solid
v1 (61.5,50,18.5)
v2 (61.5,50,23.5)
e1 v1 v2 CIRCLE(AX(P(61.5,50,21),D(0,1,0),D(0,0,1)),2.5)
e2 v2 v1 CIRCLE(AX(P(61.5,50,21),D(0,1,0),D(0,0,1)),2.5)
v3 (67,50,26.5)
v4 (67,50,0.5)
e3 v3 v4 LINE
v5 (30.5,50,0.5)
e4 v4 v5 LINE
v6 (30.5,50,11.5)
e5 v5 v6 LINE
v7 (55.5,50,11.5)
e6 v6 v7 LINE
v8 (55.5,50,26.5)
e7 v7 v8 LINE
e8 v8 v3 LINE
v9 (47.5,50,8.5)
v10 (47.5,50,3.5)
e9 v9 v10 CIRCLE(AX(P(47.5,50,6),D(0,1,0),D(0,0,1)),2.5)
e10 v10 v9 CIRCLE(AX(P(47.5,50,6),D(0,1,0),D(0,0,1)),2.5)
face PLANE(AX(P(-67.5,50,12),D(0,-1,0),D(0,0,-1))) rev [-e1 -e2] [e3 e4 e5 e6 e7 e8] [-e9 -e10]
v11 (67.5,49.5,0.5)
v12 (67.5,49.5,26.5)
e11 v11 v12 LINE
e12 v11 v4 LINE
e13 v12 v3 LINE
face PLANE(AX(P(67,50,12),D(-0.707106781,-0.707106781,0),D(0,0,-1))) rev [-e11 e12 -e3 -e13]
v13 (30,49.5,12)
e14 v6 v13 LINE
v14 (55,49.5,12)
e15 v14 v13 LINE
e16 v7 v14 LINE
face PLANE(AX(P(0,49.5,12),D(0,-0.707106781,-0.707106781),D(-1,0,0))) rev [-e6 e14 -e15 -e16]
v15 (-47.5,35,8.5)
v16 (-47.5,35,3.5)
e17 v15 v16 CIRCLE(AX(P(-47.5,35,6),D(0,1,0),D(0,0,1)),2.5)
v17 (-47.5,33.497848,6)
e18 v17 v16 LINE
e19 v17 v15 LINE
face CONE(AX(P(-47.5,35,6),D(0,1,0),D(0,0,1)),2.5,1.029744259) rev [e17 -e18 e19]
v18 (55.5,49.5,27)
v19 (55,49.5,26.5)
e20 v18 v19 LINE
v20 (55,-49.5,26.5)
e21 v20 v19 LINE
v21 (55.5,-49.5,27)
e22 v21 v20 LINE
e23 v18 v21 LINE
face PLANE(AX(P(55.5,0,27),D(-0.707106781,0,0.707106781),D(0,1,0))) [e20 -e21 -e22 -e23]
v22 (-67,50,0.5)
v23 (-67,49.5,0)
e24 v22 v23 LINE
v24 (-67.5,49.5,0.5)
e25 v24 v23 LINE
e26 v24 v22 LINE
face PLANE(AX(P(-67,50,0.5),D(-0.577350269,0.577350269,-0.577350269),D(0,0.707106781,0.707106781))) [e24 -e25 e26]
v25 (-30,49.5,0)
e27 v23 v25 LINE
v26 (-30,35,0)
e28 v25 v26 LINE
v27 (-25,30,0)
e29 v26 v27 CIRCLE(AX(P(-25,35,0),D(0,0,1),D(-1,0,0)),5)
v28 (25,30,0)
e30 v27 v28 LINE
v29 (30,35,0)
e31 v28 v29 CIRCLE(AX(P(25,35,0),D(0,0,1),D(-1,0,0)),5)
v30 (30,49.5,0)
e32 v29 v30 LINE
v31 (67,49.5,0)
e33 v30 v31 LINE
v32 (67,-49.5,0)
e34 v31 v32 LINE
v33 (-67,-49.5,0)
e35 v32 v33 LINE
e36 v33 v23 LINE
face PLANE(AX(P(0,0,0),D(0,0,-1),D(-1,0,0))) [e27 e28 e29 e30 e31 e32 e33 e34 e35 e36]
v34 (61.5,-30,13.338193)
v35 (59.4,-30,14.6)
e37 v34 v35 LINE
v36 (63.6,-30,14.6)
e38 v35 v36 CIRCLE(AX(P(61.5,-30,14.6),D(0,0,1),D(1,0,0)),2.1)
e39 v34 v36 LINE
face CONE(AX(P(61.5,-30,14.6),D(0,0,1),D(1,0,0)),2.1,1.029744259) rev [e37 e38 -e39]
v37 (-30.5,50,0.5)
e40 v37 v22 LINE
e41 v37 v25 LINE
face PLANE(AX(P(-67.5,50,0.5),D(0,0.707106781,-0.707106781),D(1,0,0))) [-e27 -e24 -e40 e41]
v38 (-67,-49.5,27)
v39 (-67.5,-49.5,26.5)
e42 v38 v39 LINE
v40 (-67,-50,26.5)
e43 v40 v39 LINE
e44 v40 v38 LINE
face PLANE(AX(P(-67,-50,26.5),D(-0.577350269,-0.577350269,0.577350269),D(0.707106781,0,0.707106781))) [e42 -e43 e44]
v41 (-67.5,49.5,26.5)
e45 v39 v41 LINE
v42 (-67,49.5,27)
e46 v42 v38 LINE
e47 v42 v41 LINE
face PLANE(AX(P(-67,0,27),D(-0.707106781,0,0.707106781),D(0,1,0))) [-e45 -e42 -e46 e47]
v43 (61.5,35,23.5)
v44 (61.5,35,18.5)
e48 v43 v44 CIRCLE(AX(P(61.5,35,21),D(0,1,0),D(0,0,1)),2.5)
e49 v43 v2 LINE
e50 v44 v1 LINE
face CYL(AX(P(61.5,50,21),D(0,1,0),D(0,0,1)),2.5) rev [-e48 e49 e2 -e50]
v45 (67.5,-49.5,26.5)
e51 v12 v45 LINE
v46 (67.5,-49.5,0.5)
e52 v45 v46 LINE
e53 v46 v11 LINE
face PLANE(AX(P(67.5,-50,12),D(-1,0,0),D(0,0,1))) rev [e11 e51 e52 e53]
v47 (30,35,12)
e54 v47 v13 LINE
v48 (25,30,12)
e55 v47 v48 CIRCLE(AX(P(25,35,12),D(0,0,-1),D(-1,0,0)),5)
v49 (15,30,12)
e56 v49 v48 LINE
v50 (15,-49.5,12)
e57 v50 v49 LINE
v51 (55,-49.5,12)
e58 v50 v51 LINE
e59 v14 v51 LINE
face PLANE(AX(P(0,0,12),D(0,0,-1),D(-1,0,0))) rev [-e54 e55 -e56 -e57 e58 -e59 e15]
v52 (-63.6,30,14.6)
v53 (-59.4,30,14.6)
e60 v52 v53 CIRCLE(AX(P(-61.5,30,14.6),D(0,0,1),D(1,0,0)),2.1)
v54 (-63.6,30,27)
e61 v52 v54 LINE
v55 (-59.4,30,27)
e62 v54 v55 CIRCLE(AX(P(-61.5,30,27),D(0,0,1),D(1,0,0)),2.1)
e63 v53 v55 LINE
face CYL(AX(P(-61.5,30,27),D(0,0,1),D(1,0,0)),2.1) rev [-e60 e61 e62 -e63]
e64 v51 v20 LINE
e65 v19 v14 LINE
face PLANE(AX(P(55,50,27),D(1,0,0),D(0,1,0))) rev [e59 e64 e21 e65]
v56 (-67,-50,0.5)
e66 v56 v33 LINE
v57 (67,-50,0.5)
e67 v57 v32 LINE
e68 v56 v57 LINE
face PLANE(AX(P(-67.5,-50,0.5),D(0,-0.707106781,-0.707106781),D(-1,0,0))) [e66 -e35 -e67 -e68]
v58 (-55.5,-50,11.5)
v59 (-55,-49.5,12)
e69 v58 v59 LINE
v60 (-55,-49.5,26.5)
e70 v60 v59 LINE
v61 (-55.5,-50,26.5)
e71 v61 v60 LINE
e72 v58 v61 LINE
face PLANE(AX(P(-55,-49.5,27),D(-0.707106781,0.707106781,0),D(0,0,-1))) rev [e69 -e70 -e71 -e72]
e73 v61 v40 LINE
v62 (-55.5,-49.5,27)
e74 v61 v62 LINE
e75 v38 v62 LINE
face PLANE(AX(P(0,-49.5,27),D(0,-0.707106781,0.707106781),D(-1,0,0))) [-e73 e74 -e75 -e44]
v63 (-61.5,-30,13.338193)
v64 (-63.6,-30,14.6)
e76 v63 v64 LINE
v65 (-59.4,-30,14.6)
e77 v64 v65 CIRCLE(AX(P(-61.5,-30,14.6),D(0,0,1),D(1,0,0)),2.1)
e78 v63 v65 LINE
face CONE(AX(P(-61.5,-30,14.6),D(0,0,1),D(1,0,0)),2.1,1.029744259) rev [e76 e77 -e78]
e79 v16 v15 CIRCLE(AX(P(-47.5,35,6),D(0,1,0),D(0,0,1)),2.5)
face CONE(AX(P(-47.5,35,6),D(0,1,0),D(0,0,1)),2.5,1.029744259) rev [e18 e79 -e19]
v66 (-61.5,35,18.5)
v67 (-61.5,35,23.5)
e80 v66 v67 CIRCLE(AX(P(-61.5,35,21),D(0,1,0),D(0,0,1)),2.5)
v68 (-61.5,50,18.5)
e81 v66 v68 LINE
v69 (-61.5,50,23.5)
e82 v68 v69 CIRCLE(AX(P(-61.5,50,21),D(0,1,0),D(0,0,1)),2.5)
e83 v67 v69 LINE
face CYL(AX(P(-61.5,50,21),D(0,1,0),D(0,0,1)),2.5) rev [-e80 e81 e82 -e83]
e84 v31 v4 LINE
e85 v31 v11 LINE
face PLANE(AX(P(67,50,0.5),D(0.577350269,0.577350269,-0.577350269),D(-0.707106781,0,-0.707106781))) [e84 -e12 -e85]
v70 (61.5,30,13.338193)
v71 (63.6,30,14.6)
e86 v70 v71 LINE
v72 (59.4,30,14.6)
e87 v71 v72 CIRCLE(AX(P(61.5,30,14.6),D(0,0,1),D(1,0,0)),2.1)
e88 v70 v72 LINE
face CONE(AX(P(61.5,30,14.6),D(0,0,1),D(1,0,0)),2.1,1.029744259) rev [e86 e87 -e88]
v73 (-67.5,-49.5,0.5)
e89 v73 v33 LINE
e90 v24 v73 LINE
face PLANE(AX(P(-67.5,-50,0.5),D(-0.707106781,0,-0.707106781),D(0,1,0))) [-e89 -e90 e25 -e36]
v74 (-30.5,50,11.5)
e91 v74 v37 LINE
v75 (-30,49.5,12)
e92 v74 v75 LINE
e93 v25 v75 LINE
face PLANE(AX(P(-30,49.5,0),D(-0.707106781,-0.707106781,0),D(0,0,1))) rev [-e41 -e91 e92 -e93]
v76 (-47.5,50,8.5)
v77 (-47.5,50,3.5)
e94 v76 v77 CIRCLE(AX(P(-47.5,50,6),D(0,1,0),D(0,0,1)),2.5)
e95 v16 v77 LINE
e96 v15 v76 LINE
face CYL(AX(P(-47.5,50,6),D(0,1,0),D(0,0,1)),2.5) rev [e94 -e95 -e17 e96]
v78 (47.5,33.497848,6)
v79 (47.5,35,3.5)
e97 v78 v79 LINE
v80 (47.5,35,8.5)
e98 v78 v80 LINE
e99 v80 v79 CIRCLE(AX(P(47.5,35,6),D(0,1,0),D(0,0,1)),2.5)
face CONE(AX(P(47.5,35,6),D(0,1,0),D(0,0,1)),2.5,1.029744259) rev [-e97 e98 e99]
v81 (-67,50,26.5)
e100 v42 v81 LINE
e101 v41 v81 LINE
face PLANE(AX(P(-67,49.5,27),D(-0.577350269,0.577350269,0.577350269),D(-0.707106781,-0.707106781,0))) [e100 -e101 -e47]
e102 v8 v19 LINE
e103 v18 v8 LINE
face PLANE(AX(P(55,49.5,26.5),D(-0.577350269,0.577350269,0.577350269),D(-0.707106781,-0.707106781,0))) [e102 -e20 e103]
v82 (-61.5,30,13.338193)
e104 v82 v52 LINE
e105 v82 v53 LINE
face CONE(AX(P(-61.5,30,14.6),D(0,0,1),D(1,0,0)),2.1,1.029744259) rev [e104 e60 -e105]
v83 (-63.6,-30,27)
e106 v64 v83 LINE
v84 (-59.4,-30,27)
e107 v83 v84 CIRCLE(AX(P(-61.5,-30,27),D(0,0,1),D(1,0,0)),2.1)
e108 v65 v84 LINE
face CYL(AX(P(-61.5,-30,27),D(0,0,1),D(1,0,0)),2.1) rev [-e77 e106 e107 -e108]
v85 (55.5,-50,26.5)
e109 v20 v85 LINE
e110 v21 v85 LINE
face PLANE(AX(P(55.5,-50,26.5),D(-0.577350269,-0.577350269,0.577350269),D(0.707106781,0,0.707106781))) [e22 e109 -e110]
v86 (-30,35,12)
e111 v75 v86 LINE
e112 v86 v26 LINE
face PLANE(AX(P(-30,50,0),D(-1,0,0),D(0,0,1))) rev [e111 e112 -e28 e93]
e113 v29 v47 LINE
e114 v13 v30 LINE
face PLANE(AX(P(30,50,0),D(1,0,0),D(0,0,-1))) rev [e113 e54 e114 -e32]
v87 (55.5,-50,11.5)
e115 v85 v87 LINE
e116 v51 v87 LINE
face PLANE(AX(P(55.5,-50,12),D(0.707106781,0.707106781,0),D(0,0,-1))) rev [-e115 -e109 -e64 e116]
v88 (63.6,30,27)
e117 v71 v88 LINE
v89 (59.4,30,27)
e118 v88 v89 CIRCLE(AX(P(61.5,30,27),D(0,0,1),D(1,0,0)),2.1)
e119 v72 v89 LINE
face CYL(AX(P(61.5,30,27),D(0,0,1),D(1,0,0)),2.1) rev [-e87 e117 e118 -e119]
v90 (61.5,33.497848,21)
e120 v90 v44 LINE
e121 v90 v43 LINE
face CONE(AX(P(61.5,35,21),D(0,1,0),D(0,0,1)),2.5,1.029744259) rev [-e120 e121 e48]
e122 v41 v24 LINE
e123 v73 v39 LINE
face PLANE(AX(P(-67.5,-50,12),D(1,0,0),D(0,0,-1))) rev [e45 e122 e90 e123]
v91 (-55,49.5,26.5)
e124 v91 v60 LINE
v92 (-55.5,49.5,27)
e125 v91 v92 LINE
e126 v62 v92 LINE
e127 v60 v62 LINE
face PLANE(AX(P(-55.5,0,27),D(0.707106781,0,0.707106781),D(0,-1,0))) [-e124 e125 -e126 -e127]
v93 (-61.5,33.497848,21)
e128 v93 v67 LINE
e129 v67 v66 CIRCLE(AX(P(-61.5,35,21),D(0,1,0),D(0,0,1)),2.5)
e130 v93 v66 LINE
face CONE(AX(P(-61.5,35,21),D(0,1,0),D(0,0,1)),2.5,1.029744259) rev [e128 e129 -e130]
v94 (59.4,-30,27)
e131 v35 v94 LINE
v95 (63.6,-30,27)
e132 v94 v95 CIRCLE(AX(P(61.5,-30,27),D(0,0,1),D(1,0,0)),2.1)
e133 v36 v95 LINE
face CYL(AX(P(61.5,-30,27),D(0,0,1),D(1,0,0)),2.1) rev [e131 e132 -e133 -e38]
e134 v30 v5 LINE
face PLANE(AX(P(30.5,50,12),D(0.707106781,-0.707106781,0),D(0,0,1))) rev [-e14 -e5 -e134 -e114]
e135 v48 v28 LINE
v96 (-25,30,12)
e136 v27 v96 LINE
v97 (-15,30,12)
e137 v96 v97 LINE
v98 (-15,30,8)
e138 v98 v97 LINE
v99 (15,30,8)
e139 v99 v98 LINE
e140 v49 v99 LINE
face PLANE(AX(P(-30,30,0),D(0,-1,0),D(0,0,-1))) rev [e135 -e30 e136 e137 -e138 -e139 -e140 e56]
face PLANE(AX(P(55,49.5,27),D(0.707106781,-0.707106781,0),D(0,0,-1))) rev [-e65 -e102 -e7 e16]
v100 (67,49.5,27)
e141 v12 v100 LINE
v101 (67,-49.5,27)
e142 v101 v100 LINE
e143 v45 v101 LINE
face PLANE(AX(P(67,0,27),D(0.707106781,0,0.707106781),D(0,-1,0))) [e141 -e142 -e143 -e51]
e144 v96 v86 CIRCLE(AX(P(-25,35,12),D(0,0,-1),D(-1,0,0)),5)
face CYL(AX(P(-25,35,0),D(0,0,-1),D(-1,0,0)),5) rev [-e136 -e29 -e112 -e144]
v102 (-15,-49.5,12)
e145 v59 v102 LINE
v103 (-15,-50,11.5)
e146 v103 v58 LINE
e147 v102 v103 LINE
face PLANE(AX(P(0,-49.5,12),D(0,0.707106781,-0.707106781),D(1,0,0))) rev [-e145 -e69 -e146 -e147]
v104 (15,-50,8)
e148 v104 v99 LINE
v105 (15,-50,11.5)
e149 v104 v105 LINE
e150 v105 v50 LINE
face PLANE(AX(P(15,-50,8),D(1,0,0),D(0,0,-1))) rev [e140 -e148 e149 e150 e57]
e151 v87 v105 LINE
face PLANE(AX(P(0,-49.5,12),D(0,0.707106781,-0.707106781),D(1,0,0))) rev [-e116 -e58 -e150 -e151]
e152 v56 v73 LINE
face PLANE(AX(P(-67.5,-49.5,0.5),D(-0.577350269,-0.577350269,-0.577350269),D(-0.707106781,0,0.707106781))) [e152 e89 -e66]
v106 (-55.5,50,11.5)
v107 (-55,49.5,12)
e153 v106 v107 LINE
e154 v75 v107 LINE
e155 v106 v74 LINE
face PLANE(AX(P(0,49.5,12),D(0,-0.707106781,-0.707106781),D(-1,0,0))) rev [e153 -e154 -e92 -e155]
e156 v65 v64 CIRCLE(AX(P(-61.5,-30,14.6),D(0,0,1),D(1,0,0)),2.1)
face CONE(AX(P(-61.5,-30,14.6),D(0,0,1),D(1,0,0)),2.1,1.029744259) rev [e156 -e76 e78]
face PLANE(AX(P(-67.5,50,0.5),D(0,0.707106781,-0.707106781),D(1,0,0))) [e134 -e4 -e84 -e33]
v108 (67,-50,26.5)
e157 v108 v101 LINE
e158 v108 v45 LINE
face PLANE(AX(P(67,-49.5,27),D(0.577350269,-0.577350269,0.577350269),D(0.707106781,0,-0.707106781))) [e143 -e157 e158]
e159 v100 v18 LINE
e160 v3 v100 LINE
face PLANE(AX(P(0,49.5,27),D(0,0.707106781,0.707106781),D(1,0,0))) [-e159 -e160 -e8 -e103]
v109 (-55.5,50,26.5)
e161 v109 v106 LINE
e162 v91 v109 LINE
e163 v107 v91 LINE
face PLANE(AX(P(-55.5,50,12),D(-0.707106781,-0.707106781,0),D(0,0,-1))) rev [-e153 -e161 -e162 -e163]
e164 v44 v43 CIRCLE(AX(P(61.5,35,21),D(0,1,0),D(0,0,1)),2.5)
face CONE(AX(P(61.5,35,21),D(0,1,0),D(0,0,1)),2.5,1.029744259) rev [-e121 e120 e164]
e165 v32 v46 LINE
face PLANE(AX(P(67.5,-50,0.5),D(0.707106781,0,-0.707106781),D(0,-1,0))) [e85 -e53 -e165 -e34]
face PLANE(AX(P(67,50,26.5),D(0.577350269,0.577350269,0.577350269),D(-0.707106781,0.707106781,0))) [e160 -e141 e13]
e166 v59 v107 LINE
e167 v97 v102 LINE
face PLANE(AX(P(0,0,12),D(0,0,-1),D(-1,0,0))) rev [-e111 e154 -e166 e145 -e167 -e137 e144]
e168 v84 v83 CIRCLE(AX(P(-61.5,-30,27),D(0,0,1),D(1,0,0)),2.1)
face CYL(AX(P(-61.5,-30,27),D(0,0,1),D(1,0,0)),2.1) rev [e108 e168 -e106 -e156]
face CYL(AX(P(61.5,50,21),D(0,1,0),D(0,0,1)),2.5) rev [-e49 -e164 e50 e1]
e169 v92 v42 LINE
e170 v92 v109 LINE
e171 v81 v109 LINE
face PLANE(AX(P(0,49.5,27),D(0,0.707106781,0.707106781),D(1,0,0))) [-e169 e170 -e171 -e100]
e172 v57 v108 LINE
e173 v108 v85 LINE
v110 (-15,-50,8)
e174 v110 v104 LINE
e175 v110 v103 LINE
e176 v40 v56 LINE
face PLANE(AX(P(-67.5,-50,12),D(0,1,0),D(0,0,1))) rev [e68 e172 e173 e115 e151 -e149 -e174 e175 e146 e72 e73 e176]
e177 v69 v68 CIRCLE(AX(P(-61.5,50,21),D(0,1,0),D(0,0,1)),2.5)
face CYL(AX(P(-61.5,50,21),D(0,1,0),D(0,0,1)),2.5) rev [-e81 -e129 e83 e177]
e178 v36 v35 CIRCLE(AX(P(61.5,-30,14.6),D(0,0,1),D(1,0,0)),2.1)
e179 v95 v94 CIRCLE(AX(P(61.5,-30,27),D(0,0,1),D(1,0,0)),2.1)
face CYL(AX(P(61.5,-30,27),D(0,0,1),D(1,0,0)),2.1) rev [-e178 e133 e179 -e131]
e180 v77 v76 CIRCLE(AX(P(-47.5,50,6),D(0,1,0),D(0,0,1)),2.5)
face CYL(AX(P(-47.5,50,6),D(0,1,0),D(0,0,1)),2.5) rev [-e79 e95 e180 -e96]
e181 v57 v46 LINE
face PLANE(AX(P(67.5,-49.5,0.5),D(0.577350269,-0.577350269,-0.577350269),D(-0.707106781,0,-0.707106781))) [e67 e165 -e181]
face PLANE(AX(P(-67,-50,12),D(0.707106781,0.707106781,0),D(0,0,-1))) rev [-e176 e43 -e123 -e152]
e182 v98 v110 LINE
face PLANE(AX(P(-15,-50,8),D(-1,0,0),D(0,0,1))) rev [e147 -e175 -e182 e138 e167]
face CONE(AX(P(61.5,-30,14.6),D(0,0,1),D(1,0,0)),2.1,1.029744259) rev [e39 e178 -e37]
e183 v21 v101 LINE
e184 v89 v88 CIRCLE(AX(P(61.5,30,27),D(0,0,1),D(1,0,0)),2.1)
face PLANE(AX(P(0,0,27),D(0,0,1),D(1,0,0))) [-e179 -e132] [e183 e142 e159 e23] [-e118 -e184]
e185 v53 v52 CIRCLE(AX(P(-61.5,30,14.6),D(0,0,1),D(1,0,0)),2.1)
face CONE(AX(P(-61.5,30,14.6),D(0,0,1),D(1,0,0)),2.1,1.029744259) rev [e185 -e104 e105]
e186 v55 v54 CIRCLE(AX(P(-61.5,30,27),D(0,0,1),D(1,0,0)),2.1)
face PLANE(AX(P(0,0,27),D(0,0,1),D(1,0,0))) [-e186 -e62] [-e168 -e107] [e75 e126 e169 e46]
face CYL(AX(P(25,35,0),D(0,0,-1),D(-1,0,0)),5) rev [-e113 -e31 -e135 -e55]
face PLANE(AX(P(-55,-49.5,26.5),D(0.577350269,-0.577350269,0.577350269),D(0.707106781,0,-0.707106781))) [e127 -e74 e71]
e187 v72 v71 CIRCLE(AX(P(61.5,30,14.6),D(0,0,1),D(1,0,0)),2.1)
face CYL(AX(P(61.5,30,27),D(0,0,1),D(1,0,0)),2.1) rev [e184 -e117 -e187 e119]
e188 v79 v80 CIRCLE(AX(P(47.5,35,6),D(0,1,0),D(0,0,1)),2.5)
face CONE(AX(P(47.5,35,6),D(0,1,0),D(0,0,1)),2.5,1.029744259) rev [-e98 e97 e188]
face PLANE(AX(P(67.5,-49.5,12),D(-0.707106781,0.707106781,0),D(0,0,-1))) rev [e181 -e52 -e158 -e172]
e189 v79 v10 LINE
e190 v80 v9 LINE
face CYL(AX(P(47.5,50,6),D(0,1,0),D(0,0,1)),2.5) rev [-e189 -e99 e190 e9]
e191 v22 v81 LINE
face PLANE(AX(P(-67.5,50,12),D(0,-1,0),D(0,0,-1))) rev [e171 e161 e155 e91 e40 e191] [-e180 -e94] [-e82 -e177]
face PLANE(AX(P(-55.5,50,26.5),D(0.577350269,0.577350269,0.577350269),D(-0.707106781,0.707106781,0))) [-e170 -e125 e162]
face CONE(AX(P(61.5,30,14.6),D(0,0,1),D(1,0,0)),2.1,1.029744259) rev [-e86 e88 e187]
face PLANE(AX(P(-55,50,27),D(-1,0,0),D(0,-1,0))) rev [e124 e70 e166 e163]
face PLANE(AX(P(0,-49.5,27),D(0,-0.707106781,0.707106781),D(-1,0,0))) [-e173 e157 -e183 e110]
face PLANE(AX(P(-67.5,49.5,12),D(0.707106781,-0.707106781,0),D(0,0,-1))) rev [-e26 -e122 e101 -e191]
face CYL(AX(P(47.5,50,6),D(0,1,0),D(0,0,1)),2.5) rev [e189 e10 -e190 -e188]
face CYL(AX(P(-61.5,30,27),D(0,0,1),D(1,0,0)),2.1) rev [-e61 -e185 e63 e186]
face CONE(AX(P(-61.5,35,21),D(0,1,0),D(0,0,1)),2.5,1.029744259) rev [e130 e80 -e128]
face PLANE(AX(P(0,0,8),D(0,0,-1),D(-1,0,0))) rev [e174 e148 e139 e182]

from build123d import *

# Parameters (mm, degrees)
SKETCH_1_W             = 135
SKETCH_1_H             = 100
EXTRUDE_1_DEPTH        = 12
SKETCH_2_W             = 12.5
SKETCH_2_H             = 100
EXTRUDE_2_DEPTH        = 15
SKETCH_3_W             = 30
SKETCH_3_H             = 200
CUT_EXTRUDE_1_DEPTH    = 4
SKETCH_4_W             = 60
SKETCH_4_H             = 20
CUT_EXTRUDE_2_DEPTH    = 86.330240829
FILLET_1_R             = 5
HOLE_WIZARD_M6_1_D     = 5
HOLE_WIZARD_M6_1_DEPTH = 15
HOLE_WIZARD_M6_1_TIP   = 1.502151548
HOLE_WIZARD_M5_1_D     = 4.2
HOLE_WIZARD_M5_1_DEPTH = 12.4
HOLE_WIZARD_M5_1_TIP   = 1.2618073
CHAMFER_1_SIZE         = 0.5


with BuildPart() as part:
    # 草图1 → 凸台-拉伸1 (new body)
    with BuildSketch(Plane.XY):
        Rectangle(SKETCH_1_W, SKETCH_1_H)
    extrude(amount=EXTRUDE_1_DEPTH)

    # 草图2 → 凸台-拉伸2 (add)
    with BuildSketch(Plane.XY.offset(12)):
        with Locations((-61.25, 0)):
            Rectangle(SKETCH_2_W, SKETCH_2_H)
        with Locations((61.25, 0)):
            Rectangle(SKETCH_2_W, SKETCH_2_H)
    extrude(amount=EXTRUDE_2_DEPTH)

    # 草图3 → 切除-拉伸1 (cut)
    with BuildSketch(Plane.XY.offset(12)):
        with Locations((0, 50)):
            Rectangle(SKETCH_3_W, SKETCH_3_H)
    extrude(amount=-CUT_EXTRUDE_1_DEPTH, mode=Mode.SUBTRACT)

    # 草图4 → 切除-拉伸2 (cut, through all)
    with BuildSketch(Plane.XY.offset(12)):
        with Locations((0, 40)):
            Rectangle(SKETCH_4_W, SKETCH_4_H)
    extrude(amount=-CUT_EXTRUDE_2_DEPTH, mode=Mode.SUBTRACT)

    # 圆角1
    fillet_1_edges = [part.edges().sort_by_distance(p)[0] for p in [
        (30, 30, 6),
        (-30, 30, 6),
    ]]
    fillet(fillet_1_edges, radius=FILLET_1_R)

    # M6 螺纹孔1
    with Locations(Plane(origin=(0, 50, 0), x_dir=(1, 0, 0), z_dir=(0, 1, 0))):
        with Locations((-61.5, -21), (-47.5, -6), (47.5, -6), (61.5, -21)):
            Hole(HOLE_WIZARD_M6_1_D / 2, depth=HOLE_WIZARD_M6_1_DEPTH)
            with Locations((0, 0, -(HOLE_WIZARD_M6_1_DEPTH + HOLE_WIZARD_M6_1_TIP / 2))):  # 118° drill point
                Cone(0, HOLE_WIZARD_M6_1_D / 2, HOLE_WIZARD_M6_1_TIP, mode=Mode.SUBTRACT)

    # M5 螺纹孔1
    with Locations(Plane.XY.offset(27)):
        with Locations((-61.5, 30), (-61.5, -30), (61.5, -30), (61.5, 30)):
            Hole(HOLE_WIZARD_M5_1_D / 2, depth=HOLE_WIZARD_M5_1_DEPTH)
            with Locations((0, 0, -(HOLE_WIZARD_M5_1_DEPTH + HOLE_WIZARD_M5_1_TIP / 2))):  # 118° drill point
                Cone(0, HOLE_WIZARD_M5_1_D / 2, HOLE_WIZARD_M5_1_TIP, mode=Mode.SUBTRACT)

    # 倒角1
    chamfer_1_edges = [part.edges().sort_by_distance(p)[0] for p in [
        (-35, -50, 12),
        (-55, -50, 19.5),
        (-55, 50, 19.5),
        (-67.5, 0, 27),
        (-61.25, -50, 27),
        (-55, 0, 27),
        (-61.25, 50, 27),
        (42.5, 50, 12),
        (55, 50, 19.5),
        (55, -50, 19.5),
        (61.25, 50, 27),
        (55, 0, 27),
        (61.25, -50, 27),
        (67.5, 0, 27),
        (35, -50, 12),
        (0, -50, 0),
        (-67.5, 0, 0),
        (48.75, 50, 0),
        (67.5, 0, 0),
        (-48.75, 50, 0),
        (-42.5, 50, 12),
        (-30, 50, 6),
        (30, 50, 6),
        (67.5, -50, 13.5),
        (-67.5, -50, 13.5),
        (-67.5, 50, 13.5),
        (67.5, 50, 13.5),
    ]]
    chamfer(chamfer_1_edges, length=CHAMFER_1_SIZE)


solid = part.part
